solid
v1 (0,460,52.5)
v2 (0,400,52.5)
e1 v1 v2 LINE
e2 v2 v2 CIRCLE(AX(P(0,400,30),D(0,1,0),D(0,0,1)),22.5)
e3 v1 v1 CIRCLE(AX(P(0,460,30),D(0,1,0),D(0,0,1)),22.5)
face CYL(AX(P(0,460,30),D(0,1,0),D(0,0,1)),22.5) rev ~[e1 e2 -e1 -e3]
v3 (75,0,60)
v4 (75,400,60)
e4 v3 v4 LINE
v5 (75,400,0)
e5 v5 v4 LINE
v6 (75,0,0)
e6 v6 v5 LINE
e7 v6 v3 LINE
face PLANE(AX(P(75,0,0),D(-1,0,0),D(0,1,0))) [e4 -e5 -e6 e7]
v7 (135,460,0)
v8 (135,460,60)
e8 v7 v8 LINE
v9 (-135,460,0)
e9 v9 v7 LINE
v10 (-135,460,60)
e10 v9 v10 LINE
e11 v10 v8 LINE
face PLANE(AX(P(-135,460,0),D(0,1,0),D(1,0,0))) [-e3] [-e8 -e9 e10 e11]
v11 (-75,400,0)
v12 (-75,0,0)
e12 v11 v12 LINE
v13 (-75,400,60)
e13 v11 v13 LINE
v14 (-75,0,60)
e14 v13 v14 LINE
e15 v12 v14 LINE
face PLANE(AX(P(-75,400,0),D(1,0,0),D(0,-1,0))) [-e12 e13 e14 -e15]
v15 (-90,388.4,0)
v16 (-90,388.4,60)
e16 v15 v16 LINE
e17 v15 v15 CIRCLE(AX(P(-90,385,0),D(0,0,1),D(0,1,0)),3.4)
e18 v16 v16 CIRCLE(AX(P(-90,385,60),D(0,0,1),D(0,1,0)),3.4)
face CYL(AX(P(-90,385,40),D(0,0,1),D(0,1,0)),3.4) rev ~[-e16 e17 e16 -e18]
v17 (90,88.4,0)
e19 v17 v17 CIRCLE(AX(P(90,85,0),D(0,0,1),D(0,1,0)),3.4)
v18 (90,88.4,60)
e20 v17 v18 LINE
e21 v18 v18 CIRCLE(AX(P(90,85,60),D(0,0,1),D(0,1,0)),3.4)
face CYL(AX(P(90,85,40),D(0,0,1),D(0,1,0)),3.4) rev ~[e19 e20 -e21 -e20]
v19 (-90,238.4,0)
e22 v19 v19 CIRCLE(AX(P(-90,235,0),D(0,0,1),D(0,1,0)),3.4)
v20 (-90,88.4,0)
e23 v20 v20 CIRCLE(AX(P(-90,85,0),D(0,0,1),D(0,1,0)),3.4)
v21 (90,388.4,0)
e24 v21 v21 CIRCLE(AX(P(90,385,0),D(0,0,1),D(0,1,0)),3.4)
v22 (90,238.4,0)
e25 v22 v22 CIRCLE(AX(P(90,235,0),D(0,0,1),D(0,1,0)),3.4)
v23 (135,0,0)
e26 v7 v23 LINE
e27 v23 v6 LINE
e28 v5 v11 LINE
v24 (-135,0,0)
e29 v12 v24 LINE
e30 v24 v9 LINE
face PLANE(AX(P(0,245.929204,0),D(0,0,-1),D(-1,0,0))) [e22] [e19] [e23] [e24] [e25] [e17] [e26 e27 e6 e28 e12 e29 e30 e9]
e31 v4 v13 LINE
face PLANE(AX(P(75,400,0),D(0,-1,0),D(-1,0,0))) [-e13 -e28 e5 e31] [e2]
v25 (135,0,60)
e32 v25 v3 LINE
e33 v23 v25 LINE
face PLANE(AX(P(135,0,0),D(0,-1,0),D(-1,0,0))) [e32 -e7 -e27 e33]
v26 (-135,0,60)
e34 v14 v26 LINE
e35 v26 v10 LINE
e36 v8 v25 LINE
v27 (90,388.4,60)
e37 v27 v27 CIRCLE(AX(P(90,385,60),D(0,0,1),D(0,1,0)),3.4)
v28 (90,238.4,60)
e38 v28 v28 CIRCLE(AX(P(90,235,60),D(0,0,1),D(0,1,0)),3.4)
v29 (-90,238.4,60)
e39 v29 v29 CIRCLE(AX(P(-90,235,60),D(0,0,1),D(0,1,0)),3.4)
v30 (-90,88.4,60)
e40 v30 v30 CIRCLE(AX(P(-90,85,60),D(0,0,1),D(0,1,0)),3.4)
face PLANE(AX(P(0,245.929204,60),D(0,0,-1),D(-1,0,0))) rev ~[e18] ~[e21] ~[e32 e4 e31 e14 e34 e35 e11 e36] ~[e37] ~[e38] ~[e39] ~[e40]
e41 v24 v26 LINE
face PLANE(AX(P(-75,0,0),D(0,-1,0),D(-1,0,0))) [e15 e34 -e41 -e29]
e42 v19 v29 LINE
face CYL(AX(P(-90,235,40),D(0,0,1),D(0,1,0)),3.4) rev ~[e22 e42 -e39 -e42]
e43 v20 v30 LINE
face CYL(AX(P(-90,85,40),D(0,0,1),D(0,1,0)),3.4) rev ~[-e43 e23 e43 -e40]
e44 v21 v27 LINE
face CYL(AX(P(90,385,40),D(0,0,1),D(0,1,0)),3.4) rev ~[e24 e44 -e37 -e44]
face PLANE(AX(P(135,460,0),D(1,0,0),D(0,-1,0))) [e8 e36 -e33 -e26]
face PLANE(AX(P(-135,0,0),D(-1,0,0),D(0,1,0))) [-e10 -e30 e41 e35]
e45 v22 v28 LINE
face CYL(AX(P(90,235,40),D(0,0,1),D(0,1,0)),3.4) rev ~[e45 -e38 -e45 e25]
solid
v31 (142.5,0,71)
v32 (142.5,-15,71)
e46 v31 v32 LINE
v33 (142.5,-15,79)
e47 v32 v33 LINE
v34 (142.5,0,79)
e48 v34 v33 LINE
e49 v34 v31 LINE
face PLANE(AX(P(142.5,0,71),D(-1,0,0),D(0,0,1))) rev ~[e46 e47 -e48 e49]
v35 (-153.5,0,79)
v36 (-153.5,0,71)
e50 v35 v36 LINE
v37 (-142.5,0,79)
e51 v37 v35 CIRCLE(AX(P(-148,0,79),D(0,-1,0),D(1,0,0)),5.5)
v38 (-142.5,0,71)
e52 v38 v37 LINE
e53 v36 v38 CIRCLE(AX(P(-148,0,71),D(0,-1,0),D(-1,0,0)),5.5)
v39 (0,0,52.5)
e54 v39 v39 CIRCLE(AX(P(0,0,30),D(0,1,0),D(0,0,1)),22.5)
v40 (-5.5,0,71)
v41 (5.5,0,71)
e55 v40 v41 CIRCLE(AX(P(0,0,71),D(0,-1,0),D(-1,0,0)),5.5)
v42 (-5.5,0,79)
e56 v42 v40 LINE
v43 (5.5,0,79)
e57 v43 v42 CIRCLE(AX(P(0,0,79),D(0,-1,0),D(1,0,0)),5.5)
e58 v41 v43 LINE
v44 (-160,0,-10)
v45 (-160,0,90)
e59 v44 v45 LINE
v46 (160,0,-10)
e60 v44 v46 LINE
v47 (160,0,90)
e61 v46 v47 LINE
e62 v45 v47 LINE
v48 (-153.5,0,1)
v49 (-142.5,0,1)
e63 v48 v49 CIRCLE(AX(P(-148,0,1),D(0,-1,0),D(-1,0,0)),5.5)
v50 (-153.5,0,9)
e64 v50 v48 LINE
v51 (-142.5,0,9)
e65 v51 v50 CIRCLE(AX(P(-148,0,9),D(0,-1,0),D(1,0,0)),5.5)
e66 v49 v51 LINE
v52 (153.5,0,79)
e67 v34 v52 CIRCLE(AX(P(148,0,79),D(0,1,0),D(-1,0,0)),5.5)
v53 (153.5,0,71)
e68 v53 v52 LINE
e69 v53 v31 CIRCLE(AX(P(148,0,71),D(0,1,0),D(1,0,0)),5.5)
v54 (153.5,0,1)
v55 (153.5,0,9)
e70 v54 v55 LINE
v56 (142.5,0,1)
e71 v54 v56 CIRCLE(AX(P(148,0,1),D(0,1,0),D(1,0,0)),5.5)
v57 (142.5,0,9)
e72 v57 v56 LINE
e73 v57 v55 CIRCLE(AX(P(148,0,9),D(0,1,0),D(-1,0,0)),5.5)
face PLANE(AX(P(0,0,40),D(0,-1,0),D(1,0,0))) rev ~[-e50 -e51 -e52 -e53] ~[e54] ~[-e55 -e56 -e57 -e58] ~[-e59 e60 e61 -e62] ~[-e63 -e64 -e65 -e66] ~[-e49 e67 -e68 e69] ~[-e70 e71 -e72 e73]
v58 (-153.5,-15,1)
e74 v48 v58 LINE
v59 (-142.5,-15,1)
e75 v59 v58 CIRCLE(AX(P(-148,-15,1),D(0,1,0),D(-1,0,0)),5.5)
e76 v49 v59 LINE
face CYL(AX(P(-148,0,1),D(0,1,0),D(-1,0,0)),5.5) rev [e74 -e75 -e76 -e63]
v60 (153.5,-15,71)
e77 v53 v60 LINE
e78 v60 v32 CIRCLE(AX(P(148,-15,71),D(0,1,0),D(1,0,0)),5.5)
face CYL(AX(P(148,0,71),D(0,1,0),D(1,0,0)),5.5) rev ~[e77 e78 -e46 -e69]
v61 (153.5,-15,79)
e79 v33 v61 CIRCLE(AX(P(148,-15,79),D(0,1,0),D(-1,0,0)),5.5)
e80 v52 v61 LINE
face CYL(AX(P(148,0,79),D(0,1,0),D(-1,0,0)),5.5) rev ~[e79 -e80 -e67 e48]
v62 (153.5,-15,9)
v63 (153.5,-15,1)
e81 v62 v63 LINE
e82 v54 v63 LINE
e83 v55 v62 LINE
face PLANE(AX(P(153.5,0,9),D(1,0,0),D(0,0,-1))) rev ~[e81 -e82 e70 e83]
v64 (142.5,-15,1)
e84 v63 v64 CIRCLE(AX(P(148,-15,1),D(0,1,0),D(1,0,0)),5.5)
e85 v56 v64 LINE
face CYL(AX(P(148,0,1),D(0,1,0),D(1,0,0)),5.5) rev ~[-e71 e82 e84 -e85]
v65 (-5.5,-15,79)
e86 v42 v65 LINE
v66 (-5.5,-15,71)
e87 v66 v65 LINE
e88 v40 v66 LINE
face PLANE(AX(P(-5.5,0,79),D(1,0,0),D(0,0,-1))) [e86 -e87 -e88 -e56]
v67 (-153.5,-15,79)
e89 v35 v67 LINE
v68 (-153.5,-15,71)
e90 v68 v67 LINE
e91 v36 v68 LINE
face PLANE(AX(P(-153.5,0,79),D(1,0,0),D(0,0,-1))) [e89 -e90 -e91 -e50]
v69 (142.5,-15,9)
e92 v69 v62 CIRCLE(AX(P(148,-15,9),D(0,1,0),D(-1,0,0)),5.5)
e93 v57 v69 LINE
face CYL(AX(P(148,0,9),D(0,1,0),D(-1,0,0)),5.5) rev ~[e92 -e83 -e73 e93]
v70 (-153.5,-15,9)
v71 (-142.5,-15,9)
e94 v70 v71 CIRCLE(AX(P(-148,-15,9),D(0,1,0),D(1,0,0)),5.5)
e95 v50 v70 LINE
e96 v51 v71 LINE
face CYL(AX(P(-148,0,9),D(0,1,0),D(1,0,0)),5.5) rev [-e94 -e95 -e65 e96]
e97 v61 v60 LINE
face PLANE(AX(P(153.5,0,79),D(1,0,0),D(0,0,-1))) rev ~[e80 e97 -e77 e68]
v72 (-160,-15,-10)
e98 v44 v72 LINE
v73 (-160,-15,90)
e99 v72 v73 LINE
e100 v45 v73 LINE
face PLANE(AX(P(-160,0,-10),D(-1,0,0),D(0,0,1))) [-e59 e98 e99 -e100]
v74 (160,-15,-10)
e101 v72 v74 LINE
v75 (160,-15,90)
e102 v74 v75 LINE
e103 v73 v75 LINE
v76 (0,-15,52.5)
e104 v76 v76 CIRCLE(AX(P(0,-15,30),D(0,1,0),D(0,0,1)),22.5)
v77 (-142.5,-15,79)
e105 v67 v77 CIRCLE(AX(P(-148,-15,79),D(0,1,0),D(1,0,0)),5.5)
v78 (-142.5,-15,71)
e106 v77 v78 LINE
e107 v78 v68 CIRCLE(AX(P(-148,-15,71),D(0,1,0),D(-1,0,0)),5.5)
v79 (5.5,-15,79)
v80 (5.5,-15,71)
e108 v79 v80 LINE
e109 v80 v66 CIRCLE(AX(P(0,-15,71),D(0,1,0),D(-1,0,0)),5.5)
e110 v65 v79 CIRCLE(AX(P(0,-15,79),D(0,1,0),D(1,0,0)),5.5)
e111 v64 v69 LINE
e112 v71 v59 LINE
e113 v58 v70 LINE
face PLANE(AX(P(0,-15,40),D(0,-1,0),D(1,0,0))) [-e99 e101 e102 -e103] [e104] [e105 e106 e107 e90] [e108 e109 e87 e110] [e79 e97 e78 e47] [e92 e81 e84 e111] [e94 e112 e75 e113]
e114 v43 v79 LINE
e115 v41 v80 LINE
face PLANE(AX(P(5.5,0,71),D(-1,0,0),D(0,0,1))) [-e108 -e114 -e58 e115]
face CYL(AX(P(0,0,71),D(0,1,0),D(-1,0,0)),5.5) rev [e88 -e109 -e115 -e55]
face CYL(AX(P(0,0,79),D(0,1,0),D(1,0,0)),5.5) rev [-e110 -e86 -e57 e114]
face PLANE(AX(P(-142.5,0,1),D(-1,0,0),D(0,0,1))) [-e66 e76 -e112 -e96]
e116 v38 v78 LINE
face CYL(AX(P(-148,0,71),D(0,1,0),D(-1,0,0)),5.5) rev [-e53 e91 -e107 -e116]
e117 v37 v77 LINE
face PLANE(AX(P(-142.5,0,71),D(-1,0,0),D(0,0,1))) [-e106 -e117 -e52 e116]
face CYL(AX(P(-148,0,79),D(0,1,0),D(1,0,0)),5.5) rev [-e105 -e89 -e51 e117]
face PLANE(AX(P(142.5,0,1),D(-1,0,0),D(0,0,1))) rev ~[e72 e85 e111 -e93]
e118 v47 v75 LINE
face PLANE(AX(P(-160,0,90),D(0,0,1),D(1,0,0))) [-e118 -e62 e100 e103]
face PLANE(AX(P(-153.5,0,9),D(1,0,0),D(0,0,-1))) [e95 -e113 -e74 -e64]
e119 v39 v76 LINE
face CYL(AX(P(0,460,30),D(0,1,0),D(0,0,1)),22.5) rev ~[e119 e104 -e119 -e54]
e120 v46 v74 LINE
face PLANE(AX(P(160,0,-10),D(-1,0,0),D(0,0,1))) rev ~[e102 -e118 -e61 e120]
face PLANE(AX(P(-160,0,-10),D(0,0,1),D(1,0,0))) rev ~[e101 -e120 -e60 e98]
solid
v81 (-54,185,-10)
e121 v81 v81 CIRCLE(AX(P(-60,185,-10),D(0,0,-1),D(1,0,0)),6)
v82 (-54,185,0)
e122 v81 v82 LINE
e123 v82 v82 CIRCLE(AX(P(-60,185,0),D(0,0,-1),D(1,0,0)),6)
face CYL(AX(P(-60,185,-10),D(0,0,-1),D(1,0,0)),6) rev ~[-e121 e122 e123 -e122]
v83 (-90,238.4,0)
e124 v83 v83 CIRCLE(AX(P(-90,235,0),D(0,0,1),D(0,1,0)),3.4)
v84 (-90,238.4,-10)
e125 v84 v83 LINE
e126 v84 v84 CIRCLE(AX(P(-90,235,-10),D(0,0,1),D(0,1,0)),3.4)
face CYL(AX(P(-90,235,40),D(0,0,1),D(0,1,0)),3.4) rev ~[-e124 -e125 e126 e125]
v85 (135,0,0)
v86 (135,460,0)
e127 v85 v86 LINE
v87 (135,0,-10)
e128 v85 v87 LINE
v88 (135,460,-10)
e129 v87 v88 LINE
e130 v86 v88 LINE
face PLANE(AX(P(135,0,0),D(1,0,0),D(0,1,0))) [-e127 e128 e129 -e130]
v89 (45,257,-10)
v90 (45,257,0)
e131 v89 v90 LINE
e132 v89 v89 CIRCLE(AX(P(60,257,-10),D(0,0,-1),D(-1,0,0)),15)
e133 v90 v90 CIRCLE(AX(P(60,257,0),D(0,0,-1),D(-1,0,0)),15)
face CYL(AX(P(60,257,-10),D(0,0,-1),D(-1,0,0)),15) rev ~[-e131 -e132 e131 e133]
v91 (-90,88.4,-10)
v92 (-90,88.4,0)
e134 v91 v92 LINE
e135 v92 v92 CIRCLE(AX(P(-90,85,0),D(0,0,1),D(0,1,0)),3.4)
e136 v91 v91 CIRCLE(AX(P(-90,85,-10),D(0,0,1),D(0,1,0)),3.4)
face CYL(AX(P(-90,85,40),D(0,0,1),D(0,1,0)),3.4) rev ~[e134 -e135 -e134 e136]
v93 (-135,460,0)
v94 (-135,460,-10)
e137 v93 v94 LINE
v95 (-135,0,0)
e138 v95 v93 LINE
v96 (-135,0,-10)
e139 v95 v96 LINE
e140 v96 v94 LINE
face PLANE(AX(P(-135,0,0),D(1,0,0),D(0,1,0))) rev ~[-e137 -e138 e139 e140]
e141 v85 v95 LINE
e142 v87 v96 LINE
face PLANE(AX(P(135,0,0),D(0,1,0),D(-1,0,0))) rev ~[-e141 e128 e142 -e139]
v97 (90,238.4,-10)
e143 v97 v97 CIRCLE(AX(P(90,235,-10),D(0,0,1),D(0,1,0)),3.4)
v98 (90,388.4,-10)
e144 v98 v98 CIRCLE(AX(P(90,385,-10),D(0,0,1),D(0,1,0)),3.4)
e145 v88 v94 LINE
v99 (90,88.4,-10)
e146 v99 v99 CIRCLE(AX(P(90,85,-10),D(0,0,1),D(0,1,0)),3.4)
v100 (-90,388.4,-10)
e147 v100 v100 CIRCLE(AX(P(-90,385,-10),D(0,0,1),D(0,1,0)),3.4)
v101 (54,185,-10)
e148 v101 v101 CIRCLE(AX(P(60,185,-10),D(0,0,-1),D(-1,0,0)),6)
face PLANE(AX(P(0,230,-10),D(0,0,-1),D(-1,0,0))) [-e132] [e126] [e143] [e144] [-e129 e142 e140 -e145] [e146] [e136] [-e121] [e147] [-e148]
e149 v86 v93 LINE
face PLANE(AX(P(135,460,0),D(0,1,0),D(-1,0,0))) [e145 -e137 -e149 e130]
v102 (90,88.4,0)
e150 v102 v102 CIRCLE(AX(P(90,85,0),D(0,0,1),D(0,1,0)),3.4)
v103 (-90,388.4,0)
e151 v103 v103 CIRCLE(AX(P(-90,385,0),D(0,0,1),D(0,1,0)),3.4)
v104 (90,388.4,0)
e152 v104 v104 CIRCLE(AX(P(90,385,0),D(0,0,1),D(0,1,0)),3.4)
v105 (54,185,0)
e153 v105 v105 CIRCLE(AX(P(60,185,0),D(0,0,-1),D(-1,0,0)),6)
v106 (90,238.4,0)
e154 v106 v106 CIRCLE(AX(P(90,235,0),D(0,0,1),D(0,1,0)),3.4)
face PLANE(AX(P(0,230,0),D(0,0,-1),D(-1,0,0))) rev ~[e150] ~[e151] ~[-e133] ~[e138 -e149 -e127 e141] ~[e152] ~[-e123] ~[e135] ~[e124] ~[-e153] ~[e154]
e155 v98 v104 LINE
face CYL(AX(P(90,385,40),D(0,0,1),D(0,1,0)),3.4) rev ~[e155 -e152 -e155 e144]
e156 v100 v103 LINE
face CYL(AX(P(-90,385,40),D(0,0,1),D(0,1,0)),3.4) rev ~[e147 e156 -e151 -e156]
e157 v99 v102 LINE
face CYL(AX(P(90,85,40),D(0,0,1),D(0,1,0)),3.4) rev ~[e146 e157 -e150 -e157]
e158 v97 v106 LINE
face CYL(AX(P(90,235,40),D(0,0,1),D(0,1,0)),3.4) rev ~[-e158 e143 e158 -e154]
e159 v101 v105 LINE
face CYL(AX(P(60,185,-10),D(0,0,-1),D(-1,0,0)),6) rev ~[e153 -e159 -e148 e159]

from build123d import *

# Parameters (mm, degrees)
BOSS_EXTRUDE1_DEPTH        = 60
SKETCH3_W                  = 270
SKETCH3_H                  = 460
BOSS_EXTRUDE3_DEPTH        = 10
SKETCH4_W                  = 320
SKETCH4_H                  = 100
BOSS_EXTRUDE4_DEPTH        = 15
SKETCH7_R                  = 5.5
CUT_EXTRUDE1_DEPTH         = 496.277699882
CUT_EXTRUDE3_DEPTH         = 496.277699882
SKETCH23_R                 = 22.5
CUT_EXTRUDE4_DEPTH         = 510.239629251
SKETCH24_R                 = 15
CUT_EXTRUDE5_DEPTH         = 498.192115786
SKETCH27_W                 = 3.4
SKETCH27_H                 = 100
M8_TAPPED_HOLE1_AT_2_COUNT = 2
M8_TAPPED_HOLE1_AT_2_PITCH = 180
M8_TAPPED_HOLE1_AT_3_COUNT = 2
M8_TAPPED_HOLE1_AT_3_PITCH = 150
M8_TAPPED_HOLE1_AT_4_COUNT = 2
M8_TAPPED_HOLE1_AT_4_PITCH = 234.307490277
M8_TAPPED_HOLE1_AT_5_COUNT = 2
M8_TAPPED_HOLE1_AT_5_PITCH = 300
M8_TAPPED_HOLE1_AT_6_COUNT = 2
M8_TAPPED_HOLE1_AT_6_PITCH = 349.857113691
SKETCH29_R                 = 6
CUT_EXTRUDE6_DEPTH         = 10


with BuildPart() as part:
    # Sketch1 → Boss-Extrude1 (new body)
    with BuildSketch(Plane.XY):
        Polygon((-135, 460), (135, 460), (135, 0), (75, 0), (75, 400), (-75, 400), (-75, 0), (-135, 0), align=None)
    extrude(amount=BOSS_EXTRUDE1_DEPTH)


with BuildPart() as body_2:
    # Sketch3 → Boss-Extrude3 (new body)
    with BuildSketch(Plane(origin=(0, 0, 0), x_dir=(-1, 0, 0), z_dir=(0, 0, -1))):
        with Locations((0, 230)):
            Rectangle(SKETCH3_W, SKETCH3_H)
    extrude(amount=BOSS_EXTRUDE3_DEPTH)

    # Sketch24 → Cut-Extrude5 (cut, through all)
    with BuildSketch(Plane(origin=(0, 0, -10), x_dir=(-1, 0, 0), z_dir=(0, 0, -1))):
        with Locations((-60, 257)):
            Circle(SKETCH24_R)
    extrude(amount=-CUT_EXTRUDE5_DEPTH, mode=Mode.SUBTRACT)


with BuildPart() as body_3:
    # Sketch4 → Boss-Extrude4 (new body)
    with BuildSketch(Plane.XZ):
        with Locations((0, 40)):
            Rectangle(SKETCH4_W, SKETCH4_H)
    extrude(amount=BOSS_EXTRUDE4_DEPTH)

    # Sketch7 → Cut-Extrude1 (cut, through all)
    with BuildSketch(Plane(origin=(0, 0, 0), x_dir=(1, 0, 0), z_dir=(0, 1, 0))):
        with Locations(Location((148, -5, 0), (0, 0, 270))):
            Circle(SKETCH7_R)
        with Locations(Location((148, -75, 0), (0, 0, 90))):
            Circle(SKETCH7_R)
        with Locations(Location((-148, -75, 0), (0, 0, 270))):
            Circle(SKETCH7_R)
        with Locations(Location((-148, -5, 0), (0, 0, 90))):
            Circle(SKETCH7_R)
        with Locations(Location((0, -75, 0), (0, 0, 270))):
            Circle(SKETCH7_R)
    extrude(amount=-CUT_EXTRUDE1_DEPTH, mode=Mode.SUBTRACT)

    # Sketch22 → Cut-Extrude3 (cut, through all)
    with BuildSketch(Plane(origin=(0, 0, 0), x_dir=(1, 0, 0), z_dir=(0, 1, 0))):
        with BuildLine():
            Line((-142.5, -1), (-142.5, -9))
            ThreePointArc((-142.5, -9), (-148, -14.5), (-153.5, -9))
            Line((-153.5, -9), (-153.5, -1))
            ThreePointArc((-153.5, -1), (-148, 4.5), (-142.5, -1))
        make_face()
        with BuildLine():
            Line((-142.5, -71), (-142.5, -79))
            ThreePointArc((-142.5, -79), (-148, -84.5), (-153.5, -79))
            Line((-153.5, -79), (-153.5, -71))
            ThreePointArc((-153.5, -71), (-148, -65.5), (-142.5, -71))
        make_face()
        with BuildLine():
            Line((142.5, -1), (142.5, -9))
            ThreePointArc((142.5, -9), (148, -14.5), (153.5, -9))
            Line((153.5, -9), (153.5, -1))
            ThreePointArc((153.5, -1), (148, 4.5), (142.5, -1))
        make_face()
        with BuildLine():
            Line((142.5, -71), (142.5, -79))
            ThreePointArc((142.5, -79), (148, -84.5), (153.5, -79))
            Line((153.5, -79), (153.5, -71))
            ThreePointArc((153.5, -71), (148, -65.5), (142.5, -71))
        make_face()
        with BuildLine():
            Line((5.5, -71), (5.5, -79))
            ThreePointArc((5.5, -79), (0, -84.5), (-5.5, -79))
            Line((-5.5, -79), (-5.5, -71))
            ThreePointArc((-5.5, -71), (0, -65.5), (5.5, -71))
        make_face()
    extrude(amount=-CUT_EXTRUDE3_DEPTH, mode=Mode.SUBTRACT)


with BuildPart() as cut_extrude4_tool:
    # Sketch23 → Cut-Extrude4 (new, through all)
    with BuildSketch(Plane(origin=(0, 460, 0), x_dir=(1, 0, 0), z_dir=(0, 1, 0))):
        with Locations(Location((0, -30, 0), (0, 0, 270))):
            Circle(SKETCH23_R)
    extrude(amount=-CUT_EXTRUDE4_DEPTH)


with BuildPart() as part_1:
    add(part.part)

    # Cut-Extrude4: cut by cut_extrude4_tool
    add(cut_extrude4_tool.part, mode=Mode.SUBTRACT)


with BuildPart() as body_3_1:
    add(body_3.part)

    # Cut-Extrude4: cut by cut_extrude4_tool
    add(cut_extrude4_tool.part, mode=Mode.SUBTRACT)


with BuildPart() as m8_tapped_hole1_tool:
    # Sketch27 → M8 Tapped Hole1 (revolve)
    with BuildSketch(Plane(origin=(90, 385, -10), x_dir=(0, 1, 0), z_dir=(1, 0, 0))):
        with Locations((1.7, 50)):
            Rectangle(SKETCH27_W, SKETCH27_H)
    m8_tapped_hole1 = revolve(axis=Axis((90, 385, -16.35), (0, 0, 1)))


with BuildPart() as part_2:
    add(part_1.part)

    # M8 Tapped Hole1: cut by m8_tapped_hole1_tool
    add(m8_tapped_hole1_tool.part, mode=Mode.SUBTRACT)


with BuildPart() as body_2_1:
    add(body_2.part)

    # M8 Tapped Hole1: cut by m8_tapped_hole1_tool
    add(m8_tapped_hole1_tool.part, mode=Mode.SUBTRACT)


with BuildPart() as m8_tapped_hole1_at_2_tool:
    # M8 Tapped Hole1 at 2: M8 Tapped Hole1 ×2
    with Locations(*[(-i * M8_TAPPED_HOLE1_AT_2_PITCH, 0, 0) for i in range(1, M8_TAPPED_HOLE1_AT_2_COUNT)]):
        add(m8_tapped_hole1)


with BuildPart() as part_3:
    add(part_2.part)

    # M8 Tapped Hole1 at 2: cut by m8_tapped_hole1_at_2_tool
    add(m8_tapped_hole1_at_2_tool.part, mode=Mode.SUBTRACT)


with BuildPart() as body_2_2:
    add(body_2_1.part)

    # M8 Tapped Hole1 at 2: cut by m8_tapped_hole1_at_2_tool
    add(m8_tapped_hole1_at_2_tool.part, mode=Mode.SUBTRACT)


with BuildPart() as m8_tapped_hole1_at_3_tool:
    # M8 Tapped Hole1 at 3: M8 Tapped Hole1 ×2
    with Locations(*[(0, -i * M8_TAPPED_HOLE1_AT_3_PITCH, 0) for i in range(1, M8_TAPPED_HOLE1_AT_3_COUNT)]):
        add(m8_tapped_hole1)


with BuildPart() as part_4:
    add(part_3.part)

    # M8 Tapped Hole1 at 3: cut by m8_tapped_hole1_at_3_tool
    add(m8_tapped_hole1_at_3_tool.part, mode=Mode.SUBTRACT)


with BuildPart() as body_2_3:
    add(body_2_2.part)

    # M8 Tapped Hole1 at 3: cut by m8_tapped_hole1_at_3_tool
    add(m8_tapped_hole1_at_3_tool.part, mode=Mode.SUBTRACT)


with BuildPart() as m8_tapped_hole1_at_4_tool:
    # M8 Tapped Hole1 at 4: M8 Tapped Hole1 ×2
    with Locations(*[Vector(-0.7682212795973759, -0.6401843996644798, 0) * (i * M8_TAPPED_HOLE1_AT_4_PITCH) for i in range(1, M8_TAPPED_HOLE1_AT_4_COUNT)]):
        add(m8_tapped_hole1)


with BuildPart() as part_5:
    add(part_4.part)

    # M8 Tapped Hole1 at 4: cut by m8_tapped_hole1_at_4_tool
    add(m8_tapped_hole1_at_4_tool.part, mode=Mode.SUBTRACT)


with BuildPart() as body_2_4:
    add(body_2_3.part)

    # M8 Tapped Hole1 at 4: cut by m8_tapped_hole1_at_4_tool
    add(m8_tapped_hole1_at_4_tool.part, mode=Mode.SUBTRACT)


with BuildPart() as m8_tapped_hole1_at_5_tool:
    # M8 Tapped Hole1 at 5: M8 Tapped Hole1 ×2
    with Locations(*[(0, -i * M8_TAPPED_HOLE1_AT_5_PITCH, 0) for i in range(1, M8_TAPPED_HOLE1_AT_5_COUNT)]):
        add(m8_tapped_hole1)


with BuildPart() as part_6:
    add(part_5.part)

    # M8 Tapped Hole1 at 5: cut by m8_tapped_hole1_at_5_tool
    add(m8_tapped_hole1_at_5_tool.part, mode=Mode.SUBTRACT)


with BuildPart() as body_2_5:
    add(body_2_4.part)

    # M8 Tapped Hole1 at 5: cut by m8_tapped_hole1_at_5_tool
    add(m8_tapped_hole1_at_5_tool.part, mode=Mode.SUBTRACT)


with BuildPart() as m8_tapped_hole1_at_6_tool:
    # M8 Tapped Hole1 at 6: M8 Tapped Hole1 ×2
    with Locations(*[Vector(-0.5144957554275266, -0.8574929257125442, 0) * (i * M8_TAPPED_HOLE1_AT_6_PITCH) for i in range(1, M8_TAPPED_HOLE1_AT_6_COUNT)]):
        add(m8_tapped_hole1)


with BuildPart() as part_7:
    add(part_6.part)

    # M8 Tapped Hole1 at 6: cut by m8_tapped_hole1_at_6_tool
    add(m8_tapped_hole1_at_6_tool.part, mode=Mode.SUBTRACT)


with BuildPart() as body_2_6:
    add(body_2_5.part)

    # M8 Tapped Hole1 at 6: cut by m8_tapped_hole1_at_6_tool
    add(m8_tapped_hole1_at_6_tool.part, mode=Mode.SUBTRACT)

    # Sketch29 → Cut-Extrude6 (cut)
    with BuildSketch(Plane(origin=(0, 0, -10), x_dir=(-1, 0, 0), z_dir=(0, 0, -1))):
        with Locations((-60, 185)):
            Circle(SKETCH29_R)
        with Locations(Location((60, 185, 0), (0, 0, 180))):
            Circle(SKETCH29_R)
    extrude(amount=-CUT_EXTRUDE6_DEPTH, mode=Mode.SUBTRACT)


solid = Compound([body_3_1.part, part_7.part, body_2_6.part])
